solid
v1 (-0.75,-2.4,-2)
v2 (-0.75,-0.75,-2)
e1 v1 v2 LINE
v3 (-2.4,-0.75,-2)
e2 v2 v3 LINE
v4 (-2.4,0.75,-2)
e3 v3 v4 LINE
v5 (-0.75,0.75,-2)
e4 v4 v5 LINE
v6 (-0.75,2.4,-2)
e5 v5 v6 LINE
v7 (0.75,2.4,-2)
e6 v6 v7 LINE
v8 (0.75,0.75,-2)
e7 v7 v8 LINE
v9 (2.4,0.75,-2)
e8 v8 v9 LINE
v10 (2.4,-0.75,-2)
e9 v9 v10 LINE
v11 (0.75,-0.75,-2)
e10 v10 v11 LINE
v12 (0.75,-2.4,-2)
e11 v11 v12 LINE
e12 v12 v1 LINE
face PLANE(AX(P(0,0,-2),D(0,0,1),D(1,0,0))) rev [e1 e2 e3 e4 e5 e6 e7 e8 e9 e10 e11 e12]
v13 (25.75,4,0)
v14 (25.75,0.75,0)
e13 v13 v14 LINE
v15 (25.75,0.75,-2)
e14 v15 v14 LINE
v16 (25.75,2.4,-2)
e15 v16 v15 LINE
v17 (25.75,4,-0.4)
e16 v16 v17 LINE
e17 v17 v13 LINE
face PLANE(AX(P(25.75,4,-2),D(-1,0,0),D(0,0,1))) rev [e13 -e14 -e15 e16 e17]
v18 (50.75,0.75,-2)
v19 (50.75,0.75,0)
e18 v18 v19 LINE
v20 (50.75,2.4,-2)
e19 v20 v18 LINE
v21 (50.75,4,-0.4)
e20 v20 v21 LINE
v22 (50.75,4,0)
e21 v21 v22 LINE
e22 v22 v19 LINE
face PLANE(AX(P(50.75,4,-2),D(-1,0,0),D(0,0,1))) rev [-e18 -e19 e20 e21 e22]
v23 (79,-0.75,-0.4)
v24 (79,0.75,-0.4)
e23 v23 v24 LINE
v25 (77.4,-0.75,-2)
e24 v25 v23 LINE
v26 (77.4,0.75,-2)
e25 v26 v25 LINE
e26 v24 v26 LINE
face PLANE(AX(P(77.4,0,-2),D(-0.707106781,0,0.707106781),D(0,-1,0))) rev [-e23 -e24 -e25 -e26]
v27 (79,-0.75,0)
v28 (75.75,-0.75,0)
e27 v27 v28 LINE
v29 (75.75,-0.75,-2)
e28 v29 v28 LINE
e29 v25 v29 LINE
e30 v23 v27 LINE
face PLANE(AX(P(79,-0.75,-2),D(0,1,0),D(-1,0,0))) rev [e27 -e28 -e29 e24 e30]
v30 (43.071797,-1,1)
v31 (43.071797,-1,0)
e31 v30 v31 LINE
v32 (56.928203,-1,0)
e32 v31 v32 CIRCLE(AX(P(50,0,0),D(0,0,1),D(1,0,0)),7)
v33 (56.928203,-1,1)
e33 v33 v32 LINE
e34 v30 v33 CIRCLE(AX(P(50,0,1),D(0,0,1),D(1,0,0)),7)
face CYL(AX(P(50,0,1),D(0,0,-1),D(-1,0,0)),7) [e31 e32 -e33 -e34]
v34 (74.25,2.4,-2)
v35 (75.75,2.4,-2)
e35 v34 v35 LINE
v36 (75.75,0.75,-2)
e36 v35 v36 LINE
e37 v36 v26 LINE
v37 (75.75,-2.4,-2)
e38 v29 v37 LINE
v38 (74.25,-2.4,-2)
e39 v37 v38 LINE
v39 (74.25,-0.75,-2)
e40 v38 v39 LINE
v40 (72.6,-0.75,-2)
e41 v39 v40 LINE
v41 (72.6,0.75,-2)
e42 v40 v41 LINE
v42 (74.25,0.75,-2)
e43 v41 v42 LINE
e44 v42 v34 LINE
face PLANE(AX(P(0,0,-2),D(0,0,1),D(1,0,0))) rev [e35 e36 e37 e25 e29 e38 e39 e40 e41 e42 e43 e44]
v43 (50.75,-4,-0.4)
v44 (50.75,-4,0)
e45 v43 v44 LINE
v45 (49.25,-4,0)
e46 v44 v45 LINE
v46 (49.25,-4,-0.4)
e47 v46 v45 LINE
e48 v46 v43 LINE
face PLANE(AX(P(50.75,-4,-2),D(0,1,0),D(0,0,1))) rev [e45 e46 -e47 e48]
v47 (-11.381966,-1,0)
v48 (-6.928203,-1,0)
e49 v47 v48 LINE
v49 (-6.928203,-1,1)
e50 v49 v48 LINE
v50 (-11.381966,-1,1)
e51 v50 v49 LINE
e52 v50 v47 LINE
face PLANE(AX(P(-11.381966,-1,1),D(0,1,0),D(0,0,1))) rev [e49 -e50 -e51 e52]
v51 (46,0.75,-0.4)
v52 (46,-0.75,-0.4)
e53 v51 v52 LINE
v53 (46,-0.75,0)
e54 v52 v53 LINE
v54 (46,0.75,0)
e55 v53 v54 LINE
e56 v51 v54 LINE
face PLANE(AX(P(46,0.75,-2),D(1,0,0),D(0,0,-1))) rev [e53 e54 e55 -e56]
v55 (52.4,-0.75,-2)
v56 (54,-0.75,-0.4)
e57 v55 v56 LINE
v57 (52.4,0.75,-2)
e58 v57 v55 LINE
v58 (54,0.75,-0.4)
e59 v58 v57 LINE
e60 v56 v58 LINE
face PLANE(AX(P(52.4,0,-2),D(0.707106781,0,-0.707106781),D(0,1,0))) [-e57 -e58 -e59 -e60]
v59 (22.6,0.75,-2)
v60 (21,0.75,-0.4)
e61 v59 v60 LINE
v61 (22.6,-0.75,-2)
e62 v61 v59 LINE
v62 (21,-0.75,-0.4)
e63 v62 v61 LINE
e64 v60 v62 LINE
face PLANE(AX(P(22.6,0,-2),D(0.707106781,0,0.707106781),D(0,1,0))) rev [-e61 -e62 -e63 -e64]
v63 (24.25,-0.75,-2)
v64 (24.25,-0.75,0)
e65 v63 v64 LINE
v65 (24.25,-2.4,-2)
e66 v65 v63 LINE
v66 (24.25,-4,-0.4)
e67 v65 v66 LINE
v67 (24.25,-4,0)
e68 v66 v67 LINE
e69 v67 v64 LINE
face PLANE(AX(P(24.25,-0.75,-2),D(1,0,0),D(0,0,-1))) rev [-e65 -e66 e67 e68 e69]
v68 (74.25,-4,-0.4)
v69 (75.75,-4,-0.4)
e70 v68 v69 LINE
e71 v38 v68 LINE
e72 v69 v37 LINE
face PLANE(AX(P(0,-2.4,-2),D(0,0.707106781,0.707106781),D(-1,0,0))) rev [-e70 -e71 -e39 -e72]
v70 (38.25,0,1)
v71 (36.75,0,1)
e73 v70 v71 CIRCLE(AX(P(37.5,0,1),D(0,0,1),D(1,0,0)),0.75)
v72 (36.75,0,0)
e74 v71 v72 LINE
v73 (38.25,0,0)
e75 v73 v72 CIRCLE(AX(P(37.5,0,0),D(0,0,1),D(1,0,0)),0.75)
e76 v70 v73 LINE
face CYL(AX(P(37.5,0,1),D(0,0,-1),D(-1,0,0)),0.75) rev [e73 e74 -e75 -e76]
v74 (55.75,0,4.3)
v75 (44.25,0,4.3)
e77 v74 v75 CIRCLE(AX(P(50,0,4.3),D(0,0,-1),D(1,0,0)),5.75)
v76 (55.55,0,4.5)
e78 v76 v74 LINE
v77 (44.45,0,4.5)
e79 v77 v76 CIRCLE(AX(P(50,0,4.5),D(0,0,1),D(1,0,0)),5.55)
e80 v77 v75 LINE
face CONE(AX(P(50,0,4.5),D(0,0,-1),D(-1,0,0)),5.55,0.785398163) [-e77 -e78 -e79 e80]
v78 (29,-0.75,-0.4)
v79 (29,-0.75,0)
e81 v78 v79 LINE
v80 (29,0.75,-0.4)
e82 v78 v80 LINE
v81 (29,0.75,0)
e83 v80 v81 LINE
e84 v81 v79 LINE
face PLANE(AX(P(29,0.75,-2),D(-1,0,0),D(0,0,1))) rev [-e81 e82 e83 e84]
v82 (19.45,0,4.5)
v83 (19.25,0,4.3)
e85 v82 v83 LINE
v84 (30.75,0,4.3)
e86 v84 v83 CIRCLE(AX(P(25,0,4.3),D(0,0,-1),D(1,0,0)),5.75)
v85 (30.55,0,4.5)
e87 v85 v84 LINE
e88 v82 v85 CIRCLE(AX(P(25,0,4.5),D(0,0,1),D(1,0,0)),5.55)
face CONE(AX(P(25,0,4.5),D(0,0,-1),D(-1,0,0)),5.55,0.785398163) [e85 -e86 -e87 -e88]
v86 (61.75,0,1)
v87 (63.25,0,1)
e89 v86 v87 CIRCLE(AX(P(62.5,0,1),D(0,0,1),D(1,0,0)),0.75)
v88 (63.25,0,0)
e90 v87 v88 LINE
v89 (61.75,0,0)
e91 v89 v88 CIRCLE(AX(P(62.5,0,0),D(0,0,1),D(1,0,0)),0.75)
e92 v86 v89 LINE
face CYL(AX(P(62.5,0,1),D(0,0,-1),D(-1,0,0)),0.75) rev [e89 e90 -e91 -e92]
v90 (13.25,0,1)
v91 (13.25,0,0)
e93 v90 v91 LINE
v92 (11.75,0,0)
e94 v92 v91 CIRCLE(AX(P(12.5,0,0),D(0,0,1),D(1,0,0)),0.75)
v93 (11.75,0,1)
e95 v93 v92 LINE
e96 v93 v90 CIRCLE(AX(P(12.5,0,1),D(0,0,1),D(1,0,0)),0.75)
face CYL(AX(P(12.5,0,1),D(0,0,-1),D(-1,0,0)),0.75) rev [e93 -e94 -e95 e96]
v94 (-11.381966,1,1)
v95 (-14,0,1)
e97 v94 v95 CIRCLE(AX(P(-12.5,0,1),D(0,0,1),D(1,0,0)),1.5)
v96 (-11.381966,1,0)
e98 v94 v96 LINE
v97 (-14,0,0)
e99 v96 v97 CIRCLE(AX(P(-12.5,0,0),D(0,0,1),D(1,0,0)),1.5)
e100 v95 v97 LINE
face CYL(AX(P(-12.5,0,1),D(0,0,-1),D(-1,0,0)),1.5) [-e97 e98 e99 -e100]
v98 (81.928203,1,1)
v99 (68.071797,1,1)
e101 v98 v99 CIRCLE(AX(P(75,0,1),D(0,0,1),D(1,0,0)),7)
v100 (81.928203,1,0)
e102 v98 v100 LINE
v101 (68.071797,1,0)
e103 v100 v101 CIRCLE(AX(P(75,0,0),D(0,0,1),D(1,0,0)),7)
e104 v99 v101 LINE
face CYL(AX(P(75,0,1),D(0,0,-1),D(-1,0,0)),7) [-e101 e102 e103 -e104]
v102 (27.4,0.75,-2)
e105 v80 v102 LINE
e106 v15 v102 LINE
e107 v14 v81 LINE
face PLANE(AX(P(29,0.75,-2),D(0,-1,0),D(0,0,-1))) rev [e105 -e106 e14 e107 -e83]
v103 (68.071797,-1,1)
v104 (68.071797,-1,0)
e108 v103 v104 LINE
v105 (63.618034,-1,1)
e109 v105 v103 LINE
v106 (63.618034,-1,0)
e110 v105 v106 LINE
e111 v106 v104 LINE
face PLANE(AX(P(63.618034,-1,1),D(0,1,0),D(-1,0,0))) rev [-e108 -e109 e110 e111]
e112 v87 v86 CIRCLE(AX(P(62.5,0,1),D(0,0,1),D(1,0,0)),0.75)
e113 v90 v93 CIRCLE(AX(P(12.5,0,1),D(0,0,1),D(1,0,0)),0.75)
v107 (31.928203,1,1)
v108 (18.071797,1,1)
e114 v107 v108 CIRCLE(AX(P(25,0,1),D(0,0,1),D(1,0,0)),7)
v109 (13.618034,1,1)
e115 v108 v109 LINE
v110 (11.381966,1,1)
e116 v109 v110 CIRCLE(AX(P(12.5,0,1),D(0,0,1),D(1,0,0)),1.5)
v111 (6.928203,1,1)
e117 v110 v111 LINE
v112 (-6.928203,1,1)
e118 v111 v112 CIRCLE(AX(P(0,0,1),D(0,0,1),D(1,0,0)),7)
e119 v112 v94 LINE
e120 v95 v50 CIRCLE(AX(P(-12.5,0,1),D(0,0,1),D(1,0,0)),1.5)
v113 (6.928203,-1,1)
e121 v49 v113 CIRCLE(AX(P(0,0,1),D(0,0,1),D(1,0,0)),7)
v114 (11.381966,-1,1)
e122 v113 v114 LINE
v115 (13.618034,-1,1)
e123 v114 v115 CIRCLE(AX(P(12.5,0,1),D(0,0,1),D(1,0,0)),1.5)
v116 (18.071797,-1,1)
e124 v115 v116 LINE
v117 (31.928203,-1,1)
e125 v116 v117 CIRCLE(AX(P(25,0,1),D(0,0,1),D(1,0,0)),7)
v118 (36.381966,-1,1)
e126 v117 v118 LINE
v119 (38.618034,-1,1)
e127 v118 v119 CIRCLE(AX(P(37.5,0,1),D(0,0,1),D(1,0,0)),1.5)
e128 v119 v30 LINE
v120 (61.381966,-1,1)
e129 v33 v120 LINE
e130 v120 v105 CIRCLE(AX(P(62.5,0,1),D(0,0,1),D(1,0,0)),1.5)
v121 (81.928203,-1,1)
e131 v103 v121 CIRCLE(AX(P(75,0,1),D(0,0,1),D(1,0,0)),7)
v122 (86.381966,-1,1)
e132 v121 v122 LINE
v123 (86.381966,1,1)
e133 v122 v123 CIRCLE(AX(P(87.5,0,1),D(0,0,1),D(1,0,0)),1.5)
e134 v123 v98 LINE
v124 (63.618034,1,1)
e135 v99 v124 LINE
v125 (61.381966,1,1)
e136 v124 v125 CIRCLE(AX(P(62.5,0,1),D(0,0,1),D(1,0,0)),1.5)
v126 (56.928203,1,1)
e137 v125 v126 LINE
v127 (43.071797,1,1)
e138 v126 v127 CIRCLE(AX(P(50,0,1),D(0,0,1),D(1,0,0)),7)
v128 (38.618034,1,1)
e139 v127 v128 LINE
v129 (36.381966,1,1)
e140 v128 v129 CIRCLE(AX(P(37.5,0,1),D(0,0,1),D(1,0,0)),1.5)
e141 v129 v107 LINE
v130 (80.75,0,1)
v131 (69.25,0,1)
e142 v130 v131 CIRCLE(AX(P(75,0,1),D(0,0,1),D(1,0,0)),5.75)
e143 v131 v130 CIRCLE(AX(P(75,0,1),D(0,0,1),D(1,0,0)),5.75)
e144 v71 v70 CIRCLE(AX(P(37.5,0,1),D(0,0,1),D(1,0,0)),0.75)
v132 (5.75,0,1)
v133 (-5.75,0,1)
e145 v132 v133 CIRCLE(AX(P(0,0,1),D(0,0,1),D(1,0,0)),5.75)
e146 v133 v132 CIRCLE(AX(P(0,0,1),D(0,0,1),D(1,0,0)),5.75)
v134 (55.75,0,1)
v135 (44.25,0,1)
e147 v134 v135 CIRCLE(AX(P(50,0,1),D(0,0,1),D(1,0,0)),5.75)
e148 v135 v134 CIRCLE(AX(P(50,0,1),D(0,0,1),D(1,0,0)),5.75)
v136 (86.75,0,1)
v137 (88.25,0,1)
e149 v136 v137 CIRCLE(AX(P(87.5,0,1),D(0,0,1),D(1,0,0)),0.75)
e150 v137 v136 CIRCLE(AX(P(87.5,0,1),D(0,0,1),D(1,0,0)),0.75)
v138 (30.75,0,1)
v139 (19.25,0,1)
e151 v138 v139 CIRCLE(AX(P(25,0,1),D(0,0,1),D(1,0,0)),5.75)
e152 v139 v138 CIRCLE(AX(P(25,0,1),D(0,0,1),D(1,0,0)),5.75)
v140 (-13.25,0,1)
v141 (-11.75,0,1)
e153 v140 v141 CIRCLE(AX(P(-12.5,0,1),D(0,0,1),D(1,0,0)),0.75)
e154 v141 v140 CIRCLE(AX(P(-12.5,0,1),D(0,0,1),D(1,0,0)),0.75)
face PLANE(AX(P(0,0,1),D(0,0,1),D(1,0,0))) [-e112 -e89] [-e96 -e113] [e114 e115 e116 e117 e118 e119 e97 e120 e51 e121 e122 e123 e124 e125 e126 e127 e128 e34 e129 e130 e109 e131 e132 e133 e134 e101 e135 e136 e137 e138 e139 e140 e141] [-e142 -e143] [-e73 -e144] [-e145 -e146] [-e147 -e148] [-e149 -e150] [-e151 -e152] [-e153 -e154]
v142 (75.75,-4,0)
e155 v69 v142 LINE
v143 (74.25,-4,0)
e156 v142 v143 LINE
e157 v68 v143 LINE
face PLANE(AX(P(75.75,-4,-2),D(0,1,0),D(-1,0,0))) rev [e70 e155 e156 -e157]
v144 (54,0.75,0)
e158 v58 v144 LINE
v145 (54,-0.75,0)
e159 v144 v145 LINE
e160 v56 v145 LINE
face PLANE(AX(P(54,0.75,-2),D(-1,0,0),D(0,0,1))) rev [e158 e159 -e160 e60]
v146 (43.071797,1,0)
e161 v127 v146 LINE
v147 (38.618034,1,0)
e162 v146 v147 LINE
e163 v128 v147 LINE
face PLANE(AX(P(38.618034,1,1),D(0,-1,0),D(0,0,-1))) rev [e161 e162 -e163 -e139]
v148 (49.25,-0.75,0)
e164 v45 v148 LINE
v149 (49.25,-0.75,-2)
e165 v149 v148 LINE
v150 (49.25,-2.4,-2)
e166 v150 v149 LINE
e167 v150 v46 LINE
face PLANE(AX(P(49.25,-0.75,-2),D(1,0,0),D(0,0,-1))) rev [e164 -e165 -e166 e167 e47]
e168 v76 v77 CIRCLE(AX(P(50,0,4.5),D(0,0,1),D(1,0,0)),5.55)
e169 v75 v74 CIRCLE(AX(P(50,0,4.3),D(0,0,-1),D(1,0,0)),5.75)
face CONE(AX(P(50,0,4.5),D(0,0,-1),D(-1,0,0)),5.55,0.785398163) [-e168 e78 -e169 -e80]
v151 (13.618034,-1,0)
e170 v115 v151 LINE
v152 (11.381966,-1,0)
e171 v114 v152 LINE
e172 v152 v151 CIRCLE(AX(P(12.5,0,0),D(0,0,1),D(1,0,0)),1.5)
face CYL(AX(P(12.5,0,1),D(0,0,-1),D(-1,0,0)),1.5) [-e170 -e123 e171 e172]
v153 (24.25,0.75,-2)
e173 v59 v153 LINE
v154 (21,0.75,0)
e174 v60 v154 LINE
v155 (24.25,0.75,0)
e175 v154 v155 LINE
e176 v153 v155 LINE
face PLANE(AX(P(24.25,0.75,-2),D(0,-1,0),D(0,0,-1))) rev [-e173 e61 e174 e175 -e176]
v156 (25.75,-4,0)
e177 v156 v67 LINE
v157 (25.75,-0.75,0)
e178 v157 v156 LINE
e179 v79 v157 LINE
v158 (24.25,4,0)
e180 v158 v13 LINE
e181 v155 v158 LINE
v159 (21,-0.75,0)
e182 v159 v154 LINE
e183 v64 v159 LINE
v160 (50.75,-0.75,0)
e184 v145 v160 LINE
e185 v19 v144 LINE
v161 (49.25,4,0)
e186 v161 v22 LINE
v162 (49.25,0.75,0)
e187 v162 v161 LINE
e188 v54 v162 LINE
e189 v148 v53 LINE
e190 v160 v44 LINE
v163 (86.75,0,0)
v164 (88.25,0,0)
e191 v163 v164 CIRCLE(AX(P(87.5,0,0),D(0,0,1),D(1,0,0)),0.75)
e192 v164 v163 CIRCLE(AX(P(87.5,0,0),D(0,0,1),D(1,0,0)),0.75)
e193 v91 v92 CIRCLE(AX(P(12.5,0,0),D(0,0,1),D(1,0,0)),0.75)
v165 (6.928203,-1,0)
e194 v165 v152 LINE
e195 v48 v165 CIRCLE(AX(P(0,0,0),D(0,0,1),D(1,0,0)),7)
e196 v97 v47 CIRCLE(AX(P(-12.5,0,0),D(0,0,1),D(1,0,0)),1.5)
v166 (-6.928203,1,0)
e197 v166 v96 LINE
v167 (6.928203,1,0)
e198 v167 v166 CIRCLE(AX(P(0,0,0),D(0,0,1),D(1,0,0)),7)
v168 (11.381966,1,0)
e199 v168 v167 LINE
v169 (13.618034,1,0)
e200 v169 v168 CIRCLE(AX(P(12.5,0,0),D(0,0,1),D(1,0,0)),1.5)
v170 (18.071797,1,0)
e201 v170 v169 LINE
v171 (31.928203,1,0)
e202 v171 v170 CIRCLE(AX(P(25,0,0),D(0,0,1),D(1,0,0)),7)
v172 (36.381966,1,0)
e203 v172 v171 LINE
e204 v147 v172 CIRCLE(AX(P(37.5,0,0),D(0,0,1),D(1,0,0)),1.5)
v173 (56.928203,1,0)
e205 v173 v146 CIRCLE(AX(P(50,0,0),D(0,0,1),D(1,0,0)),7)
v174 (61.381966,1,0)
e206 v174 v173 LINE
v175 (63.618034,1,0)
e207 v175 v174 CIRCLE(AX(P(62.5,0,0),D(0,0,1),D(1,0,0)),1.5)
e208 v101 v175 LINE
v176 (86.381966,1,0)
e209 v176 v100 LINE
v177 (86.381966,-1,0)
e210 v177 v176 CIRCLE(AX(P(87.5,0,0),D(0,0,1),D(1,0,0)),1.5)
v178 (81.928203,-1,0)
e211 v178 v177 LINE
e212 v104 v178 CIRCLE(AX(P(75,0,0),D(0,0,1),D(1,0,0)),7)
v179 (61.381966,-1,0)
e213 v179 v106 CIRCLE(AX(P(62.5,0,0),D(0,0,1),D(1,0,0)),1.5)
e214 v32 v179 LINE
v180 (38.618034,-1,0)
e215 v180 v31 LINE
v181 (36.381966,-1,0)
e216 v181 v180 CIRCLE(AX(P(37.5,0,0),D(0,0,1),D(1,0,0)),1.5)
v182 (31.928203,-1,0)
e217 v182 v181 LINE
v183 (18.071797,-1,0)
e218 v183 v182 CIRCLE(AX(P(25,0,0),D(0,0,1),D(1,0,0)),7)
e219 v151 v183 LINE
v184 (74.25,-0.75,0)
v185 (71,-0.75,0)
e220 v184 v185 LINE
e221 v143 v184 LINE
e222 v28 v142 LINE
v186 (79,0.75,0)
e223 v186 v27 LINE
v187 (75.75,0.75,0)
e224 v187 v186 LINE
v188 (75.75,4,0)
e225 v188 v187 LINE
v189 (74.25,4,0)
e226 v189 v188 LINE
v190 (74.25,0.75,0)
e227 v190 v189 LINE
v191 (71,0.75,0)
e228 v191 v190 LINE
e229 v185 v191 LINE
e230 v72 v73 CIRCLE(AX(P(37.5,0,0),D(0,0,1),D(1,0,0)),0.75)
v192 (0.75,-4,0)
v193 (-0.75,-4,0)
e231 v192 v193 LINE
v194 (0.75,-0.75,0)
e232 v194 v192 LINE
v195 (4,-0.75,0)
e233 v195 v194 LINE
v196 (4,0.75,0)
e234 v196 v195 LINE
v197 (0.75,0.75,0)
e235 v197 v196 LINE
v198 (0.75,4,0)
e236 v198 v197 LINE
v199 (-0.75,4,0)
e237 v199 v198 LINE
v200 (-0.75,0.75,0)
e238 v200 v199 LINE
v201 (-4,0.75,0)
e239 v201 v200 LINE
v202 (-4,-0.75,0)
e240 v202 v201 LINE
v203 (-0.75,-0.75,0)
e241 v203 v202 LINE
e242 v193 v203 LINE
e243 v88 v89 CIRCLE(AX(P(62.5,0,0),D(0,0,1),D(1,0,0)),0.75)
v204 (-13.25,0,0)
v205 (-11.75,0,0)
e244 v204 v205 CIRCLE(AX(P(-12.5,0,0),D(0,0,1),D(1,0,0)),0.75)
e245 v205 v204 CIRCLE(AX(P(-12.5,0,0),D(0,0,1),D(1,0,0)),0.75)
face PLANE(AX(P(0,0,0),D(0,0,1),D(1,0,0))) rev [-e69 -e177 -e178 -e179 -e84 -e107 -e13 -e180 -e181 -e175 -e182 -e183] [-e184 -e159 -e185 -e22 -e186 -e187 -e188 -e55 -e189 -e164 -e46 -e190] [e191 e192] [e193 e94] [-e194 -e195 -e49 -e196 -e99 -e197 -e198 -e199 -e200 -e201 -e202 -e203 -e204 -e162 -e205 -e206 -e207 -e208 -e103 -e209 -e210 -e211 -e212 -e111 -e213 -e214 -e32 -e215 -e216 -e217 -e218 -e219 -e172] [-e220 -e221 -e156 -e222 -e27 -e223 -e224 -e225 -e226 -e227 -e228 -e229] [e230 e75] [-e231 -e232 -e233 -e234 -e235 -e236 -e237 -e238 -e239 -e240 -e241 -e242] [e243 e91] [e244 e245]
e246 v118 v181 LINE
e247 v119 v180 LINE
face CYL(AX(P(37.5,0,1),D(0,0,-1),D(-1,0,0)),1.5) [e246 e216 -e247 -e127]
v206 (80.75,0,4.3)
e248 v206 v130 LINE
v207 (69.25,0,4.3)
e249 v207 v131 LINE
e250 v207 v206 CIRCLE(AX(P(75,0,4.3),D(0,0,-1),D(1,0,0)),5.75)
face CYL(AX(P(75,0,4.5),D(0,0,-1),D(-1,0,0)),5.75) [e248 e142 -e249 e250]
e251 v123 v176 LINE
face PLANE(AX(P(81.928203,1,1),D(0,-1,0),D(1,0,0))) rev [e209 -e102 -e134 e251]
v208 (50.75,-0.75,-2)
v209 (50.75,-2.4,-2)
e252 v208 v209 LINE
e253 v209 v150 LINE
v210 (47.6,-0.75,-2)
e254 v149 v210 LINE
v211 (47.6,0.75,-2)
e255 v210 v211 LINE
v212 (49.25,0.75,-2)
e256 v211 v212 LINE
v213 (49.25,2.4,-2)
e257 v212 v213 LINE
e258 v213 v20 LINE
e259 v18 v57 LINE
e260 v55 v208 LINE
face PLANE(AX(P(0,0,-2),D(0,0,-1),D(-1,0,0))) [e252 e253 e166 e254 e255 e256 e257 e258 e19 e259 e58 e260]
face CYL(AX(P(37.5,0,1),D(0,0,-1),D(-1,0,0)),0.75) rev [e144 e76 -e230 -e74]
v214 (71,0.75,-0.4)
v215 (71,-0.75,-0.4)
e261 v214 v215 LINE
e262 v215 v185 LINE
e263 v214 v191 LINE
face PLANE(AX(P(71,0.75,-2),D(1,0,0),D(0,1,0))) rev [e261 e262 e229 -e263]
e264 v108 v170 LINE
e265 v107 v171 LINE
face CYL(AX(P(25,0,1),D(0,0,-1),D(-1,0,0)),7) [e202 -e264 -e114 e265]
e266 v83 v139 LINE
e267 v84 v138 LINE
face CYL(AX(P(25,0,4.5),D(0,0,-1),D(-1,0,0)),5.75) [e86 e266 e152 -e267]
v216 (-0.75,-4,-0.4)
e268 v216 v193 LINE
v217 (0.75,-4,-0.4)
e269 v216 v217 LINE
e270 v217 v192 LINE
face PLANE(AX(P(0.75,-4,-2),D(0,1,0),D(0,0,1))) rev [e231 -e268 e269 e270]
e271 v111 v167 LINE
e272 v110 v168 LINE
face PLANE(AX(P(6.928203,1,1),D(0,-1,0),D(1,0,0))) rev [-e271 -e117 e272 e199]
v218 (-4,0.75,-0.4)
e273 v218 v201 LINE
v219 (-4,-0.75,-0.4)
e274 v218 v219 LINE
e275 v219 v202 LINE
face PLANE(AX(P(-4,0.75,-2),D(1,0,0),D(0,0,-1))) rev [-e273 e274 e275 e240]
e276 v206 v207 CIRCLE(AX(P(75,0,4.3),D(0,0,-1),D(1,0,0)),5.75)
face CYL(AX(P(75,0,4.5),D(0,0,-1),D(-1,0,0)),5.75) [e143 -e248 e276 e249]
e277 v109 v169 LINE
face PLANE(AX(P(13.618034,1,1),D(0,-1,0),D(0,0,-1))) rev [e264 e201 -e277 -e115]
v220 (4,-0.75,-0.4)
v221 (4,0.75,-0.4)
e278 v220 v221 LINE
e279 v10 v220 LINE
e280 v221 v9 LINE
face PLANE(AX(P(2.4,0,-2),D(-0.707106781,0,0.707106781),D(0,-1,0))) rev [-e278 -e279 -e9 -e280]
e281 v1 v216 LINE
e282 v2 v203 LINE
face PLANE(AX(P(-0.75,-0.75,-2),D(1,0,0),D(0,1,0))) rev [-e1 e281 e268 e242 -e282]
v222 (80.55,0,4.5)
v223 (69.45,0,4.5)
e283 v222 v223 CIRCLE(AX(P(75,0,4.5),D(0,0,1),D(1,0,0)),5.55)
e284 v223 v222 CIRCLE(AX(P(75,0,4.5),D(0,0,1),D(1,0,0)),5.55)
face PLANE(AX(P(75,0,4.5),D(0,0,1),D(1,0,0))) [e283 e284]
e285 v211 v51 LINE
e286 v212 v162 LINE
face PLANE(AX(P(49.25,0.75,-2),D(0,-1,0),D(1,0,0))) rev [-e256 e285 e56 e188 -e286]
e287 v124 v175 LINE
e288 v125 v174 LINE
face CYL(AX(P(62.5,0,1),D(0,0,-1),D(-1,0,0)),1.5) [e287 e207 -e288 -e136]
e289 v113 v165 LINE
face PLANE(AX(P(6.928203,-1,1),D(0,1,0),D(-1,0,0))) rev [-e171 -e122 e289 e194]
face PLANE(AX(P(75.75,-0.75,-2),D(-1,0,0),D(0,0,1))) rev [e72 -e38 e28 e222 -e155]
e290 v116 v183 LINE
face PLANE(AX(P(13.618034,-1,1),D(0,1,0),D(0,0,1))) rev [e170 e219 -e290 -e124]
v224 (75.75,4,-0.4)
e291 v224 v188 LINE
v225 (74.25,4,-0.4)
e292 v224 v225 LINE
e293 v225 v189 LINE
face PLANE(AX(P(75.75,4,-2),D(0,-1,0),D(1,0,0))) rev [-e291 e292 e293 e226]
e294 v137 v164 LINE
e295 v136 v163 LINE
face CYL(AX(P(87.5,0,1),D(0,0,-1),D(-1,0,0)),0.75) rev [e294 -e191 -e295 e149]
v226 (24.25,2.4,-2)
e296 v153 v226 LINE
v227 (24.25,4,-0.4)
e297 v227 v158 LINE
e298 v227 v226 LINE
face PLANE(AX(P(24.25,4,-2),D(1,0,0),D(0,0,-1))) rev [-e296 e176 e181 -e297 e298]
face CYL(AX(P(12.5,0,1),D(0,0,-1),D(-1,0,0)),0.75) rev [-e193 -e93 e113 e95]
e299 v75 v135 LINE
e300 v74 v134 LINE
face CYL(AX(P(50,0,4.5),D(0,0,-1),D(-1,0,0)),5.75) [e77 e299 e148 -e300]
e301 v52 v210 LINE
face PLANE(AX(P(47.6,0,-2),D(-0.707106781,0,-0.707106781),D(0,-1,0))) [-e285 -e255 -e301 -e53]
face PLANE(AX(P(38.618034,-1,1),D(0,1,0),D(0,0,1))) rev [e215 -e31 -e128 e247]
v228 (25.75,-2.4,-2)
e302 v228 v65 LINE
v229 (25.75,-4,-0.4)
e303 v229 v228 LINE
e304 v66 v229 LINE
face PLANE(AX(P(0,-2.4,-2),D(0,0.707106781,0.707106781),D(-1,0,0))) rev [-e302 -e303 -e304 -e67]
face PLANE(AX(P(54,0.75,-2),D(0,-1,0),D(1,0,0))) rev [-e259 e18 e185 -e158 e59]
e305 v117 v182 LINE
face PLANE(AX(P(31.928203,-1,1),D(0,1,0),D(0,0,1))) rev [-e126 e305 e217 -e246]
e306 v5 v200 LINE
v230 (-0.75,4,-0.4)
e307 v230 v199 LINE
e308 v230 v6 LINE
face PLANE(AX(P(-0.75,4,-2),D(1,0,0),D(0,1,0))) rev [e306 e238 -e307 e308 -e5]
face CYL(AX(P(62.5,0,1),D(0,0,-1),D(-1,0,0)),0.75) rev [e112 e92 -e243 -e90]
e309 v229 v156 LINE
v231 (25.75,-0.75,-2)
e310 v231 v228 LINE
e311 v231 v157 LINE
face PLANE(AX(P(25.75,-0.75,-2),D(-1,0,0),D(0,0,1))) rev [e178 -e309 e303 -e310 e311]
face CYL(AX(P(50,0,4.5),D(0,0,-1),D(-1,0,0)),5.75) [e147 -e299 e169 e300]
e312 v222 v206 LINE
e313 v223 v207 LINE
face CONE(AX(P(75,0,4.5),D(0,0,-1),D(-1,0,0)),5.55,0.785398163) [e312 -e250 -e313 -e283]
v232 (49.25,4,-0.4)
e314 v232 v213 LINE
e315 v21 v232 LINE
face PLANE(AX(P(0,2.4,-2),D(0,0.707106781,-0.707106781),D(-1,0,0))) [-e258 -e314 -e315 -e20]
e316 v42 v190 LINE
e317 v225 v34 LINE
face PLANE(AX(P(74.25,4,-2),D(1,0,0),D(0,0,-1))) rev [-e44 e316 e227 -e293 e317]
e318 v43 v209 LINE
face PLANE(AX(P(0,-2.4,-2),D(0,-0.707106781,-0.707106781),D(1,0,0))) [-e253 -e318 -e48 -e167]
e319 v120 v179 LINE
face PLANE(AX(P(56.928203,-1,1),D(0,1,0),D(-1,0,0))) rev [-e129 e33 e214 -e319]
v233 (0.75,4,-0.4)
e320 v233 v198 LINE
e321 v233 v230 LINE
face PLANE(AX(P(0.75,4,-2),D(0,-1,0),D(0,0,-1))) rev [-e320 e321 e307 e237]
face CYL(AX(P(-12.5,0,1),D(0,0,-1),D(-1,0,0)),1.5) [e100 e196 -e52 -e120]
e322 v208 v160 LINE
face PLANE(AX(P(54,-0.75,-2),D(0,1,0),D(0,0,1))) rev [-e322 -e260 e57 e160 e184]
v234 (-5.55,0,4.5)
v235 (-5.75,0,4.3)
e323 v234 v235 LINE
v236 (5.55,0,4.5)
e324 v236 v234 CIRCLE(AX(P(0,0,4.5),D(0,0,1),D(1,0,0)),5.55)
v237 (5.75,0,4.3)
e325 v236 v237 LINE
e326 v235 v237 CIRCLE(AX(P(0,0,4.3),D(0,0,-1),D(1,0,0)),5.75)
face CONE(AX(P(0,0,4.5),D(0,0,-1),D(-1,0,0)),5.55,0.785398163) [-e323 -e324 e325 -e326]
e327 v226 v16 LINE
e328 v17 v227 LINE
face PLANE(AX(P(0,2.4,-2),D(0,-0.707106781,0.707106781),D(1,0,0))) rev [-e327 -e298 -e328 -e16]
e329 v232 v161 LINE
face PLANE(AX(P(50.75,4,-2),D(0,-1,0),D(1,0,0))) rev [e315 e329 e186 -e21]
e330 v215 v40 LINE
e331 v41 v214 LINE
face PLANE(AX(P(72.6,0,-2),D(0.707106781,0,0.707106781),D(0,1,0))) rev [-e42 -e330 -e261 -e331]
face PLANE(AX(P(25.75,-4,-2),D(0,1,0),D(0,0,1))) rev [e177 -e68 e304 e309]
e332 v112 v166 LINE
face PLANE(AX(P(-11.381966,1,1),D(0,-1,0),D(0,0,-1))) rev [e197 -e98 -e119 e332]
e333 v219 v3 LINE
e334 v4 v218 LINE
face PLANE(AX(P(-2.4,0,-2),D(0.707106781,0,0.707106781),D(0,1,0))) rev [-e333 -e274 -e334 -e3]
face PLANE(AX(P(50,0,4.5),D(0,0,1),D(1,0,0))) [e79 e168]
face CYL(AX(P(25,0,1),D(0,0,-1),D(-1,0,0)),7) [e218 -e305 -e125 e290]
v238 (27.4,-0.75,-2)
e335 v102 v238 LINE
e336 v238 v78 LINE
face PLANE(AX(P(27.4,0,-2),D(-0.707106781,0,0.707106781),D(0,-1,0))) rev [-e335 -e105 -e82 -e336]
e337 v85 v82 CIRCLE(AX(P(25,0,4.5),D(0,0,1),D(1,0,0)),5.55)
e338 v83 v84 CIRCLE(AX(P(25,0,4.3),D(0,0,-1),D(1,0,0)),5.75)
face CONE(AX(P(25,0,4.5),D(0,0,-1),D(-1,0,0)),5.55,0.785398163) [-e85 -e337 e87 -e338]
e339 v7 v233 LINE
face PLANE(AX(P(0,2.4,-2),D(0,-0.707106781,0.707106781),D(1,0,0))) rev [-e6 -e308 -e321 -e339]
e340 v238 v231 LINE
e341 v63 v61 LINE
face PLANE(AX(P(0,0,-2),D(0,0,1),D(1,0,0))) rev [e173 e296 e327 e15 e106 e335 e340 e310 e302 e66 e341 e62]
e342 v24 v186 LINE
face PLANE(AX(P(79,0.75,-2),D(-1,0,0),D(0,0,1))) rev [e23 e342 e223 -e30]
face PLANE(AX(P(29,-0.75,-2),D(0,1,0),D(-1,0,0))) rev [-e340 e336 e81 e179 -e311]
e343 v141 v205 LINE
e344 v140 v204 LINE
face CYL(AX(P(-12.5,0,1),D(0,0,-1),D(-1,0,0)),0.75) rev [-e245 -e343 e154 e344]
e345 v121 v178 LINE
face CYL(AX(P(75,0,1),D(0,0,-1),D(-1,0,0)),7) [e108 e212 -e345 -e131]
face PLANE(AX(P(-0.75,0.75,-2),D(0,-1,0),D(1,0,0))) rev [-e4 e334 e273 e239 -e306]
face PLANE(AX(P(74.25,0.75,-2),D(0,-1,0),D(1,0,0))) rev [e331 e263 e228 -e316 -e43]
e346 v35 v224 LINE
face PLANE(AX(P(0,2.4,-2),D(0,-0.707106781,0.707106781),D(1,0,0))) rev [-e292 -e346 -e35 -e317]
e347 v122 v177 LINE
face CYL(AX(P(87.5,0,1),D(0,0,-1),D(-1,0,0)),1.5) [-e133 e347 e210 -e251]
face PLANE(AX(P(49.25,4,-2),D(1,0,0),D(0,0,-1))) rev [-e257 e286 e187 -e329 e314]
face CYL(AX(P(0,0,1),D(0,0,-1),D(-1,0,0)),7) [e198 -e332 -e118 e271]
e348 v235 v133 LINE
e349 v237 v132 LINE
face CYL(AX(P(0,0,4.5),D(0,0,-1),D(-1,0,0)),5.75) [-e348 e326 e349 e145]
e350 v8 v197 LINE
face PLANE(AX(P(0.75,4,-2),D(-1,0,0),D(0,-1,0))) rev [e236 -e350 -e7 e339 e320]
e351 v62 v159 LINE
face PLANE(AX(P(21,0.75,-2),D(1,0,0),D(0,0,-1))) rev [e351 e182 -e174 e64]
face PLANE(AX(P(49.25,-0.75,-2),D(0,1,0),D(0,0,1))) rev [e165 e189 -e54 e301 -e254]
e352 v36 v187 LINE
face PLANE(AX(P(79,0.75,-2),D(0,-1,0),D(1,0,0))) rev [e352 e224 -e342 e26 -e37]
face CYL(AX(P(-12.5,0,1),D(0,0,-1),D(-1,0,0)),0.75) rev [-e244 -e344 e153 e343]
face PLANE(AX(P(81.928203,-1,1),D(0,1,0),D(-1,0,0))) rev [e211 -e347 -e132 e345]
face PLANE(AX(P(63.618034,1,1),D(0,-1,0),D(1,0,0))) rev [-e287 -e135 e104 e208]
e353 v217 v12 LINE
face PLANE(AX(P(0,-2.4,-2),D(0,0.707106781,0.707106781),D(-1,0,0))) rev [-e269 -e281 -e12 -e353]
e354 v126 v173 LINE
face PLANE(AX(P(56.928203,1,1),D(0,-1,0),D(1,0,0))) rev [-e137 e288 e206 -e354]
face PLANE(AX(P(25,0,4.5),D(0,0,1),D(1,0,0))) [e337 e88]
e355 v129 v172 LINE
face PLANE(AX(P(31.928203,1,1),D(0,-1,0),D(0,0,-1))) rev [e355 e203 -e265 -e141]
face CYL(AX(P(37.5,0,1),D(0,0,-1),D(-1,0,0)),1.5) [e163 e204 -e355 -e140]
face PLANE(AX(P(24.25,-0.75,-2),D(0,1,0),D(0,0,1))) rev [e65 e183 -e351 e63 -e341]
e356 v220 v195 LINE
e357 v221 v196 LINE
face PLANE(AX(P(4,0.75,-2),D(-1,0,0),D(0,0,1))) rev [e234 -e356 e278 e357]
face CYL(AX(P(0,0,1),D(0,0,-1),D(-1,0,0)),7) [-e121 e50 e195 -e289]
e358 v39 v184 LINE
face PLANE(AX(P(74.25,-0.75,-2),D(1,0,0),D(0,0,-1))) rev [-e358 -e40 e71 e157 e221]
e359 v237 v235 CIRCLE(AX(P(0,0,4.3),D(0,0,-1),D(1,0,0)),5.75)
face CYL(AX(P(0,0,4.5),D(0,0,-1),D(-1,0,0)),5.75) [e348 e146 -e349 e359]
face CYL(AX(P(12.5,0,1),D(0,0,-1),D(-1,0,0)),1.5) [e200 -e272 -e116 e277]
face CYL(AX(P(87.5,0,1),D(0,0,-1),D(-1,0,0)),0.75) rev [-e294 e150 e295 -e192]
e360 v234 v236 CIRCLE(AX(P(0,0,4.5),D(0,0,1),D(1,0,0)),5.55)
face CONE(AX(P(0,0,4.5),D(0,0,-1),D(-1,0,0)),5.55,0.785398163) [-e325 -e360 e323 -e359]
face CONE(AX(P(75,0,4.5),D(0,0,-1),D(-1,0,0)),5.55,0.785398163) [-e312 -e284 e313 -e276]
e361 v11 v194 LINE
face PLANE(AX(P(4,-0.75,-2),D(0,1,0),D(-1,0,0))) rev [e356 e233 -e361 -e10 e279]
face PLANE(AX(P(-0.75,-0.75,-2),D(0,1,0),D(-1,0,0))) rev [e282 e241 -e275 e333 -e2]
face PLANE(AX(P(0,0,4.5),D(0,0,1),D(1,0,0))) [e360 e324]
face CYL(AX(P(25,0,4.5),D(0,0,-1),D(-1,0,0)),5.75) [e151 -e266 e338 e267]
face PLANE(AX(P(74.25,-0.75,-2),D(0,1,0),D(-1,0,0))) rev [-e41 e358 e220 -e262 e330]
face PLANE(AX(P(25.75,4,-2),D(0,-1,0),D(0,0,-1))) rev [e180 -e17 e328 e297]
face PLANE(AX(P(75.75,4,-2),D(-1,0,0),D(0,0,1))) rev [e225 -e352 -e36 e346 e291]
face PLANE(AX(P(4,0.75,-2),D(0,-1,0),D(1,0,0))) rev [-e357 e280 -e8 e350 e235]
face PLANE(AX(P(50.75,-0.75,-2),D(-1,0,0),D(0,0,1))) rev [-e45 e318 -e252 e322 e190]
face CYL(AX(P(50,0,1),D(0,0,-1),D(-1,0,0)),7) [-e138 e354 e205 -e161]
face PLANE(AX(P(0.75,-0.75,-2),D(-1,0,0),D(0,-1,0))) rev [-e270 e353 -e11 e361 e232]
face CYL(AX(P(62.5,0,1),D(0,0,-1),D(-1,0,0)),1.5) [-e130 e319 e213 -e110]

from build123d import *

# Parameters (mm, degrees)
SKETCH1_R           = 0.75
BOSS_EXTRUDE1_DEPTH = 1
SKETCH2_R           = 5.75
BOSS_EXTRUDE2_DEPTH = 3.5
CHAMFER1_SIZE       = 0.2
BOSS_EXTRUDE3_DEPTH = 2
CHAMFER2_SIZE       = 1.6


with BuildPart() as part:
    # Sketch1 → Boss-Extrude1 (new body)
    with BuildSketch(Plane.XY):
        with BuildLine():
            Line((-11.381966011, 1), (-6.92820323, 1))
            ThreePointArc((-6.92820323, 1), (0, 7), (6.92820323, 1))
            Line((6.92820323, 1), (11.381966011, 1))
            ThreePointArc((11.381966011, 1), (12.5, 1.5), (13.618033989, 1))
            Line((13.618033989, 1), (18.07179677, 1))
            ThreePointArc((18.07179677, 1), (25, 7), (31.92820323, 1))
            Line((31.92820323, 1), (36.381966011, 1))
            ThreePointArc((36.381966011, 1), (37.5, 1.5), (38.618033989, 1))
            Line((38.618033989, 1), (43.07179677, 1))
            ThreePointArc((43.07179677, 1), (50, 7), (56.92820323, 1))
            Line((56.92820323, 1), (61.381966011, 1))
            ThreePointArc((61.381966011, 1), (62.5, 1.5), (63.618033989, 1))
            Line((63.618033989, 1), (68.07179677, 1))
            ThreePointArc((68.07179677, 1), (75, 7), (81.92820323, 1))
            Line((81.92820323, 1), (86.381966011, 1))
            ThreePointArc((86.381966011, 1), (89, 0), (86.381966011, -1))
            Line((86.381966011, -1), (81.92820323, -1))
            ThreePointArc((81.92820323, -1), (75, -7), (68.07179677, -1))
            Line((68.07179677, -1), (63.618033989, -1))
            ThreePointArc((63.618033989, -1), (62.5, -1.5), (61.381966011, -1))
            Line((61.381966011, -1), (56.92820323, -1))
            ThreePointArc((56.92820323, -1), (50, -7), (43.07179677, -1))
            Line((43.07179677, -1), (38.618033989, -1))
            ThreePointArc((38.618033989, -1), (37.5, -1.5), (36.381966011, -1))
            Line((36.381966011, -1), (31.92820323, -1))
            ThreePointArc((31.92820323, -1), (25, -7), (18.07179677, -1))
            Line((18.07179677, -1), (13.618033989, -1))
            ThreePointArc((13.618033989, -1), (12.5, -1.5), (11.381966011, -1))
            Line((11.381966011, -1), (6.92820323, -1))
            ThreePointArc((6.92820323, -1), (0, -7), (-6.92820323, -1))
            Line((-6.92820323, -1), (-11.381966011, -1))
            ThreePointArc((-11.381966011, -1), (-14, 0), (-11.381966011, 1))
        make_face()
        with Locations((12.5, 0)):
            Circle(SKETCH1_R, mode=Mode.SUBTRACT)
        with Locations((37.5, 0)):
            Circle(SKETCH1_R, mode=Mode.SUBTRACT)
        with Locations((62.5, 0)):
            Circle(SKETCH1_R, mode=Mode.SUBTRACT)
        with Locations((-12.5, 0)):
            Circle(SKETCH1_R, mode=Mode.SUBTRACT)
        with Locations((87.5, 0)):
            Circle(SKETCH1_R, mode=Mode.SUBTRACT)
    extrude(amount=BOSS_EXTRUDE1_DEPTH)

    # Sketch2 → Boss-Extrude2 (add)
    with BuildSketch(Plane.XY.offset(1)):
        Circle(SKETCH2_R)
        with Locations((25, 0)):
            Circle(SKETCH2_R)
        with Locations((50, 0)):
            Circle(SKETCH2_R)
        with Locations((75, 0)):
            Circle(SKETCH2_R)
    extrude(amount=BOSS_EXTRUDE2_DEPTH)

    # Chamfer1
    chamfer1_edges = [part.edges().sort_by_distance(p)[0] for p in [
        (-5.75, 0, 4.5),
        (19.25, 0, 4.5),
        (44.25, 0, 4.5),
        (69.25, 0, 4.5),
    ]]
    chamfer(chamfer1_edges, length=CHAMFER1_SIZE)

    # Sketch3 → Boss-Extrude3 (add)
    with BuildSketch(Plane(origin=(0, 0, 0), x_dir=(-1, 0, 0), z_dir=(0, 0, -1))):
        Polygon((-74.25, -0.75), (-74.25, -4), (-75.75, -4), (-75.75, -0.75), (-79, -0.75), (-79, 0.75), (-75.75, 0.75), (-75.75, 4), (-74.25, 4), (-74.25, 0.75), (-71, 0.75), (-71, -0.75), align=None)
        Polygon((-50.75, 4), (-49.25, 4), (-49.25, 0.75), (-46, 0.75), (-46, -0.75), (-49.25, -0.75), (-49.25, -4), (-50.75, -4), (-50.75, -0.75), (-54, -0.75), (-54, 0.75), (-50.75, 0.75), align=None)
        Polygon((-29, 0.75), (-25.75, 0.75), (-25.75, 4), (-24.25, 4), (-24.25, 0.75), (-21, 0.75), (-21, -0.75), (-24.25, -0.75), (-24.25, -4), (-25.75, -4), (-25.75, -0.75), (-29, -0.75), align=None)
        Polygon((-4, 0.75), (-0.75, 0.75), (-0.75, 4), (0.75, 4), (0.75, 0.75), (4, 0.75), (4, -0.75), (0.75, -0.75), (0.75, -4), (-0.75, -4), (-0.75, -0.75), (-4, -0.75), align=None)
    extrude(amount=BOSS_EXTRUDE3_DEPTH)

    # Chamfer2
    chamfer2_edges = [part.edges().sort_by_distance(p)[0] for p in [
        (75, -4, -2),
        (71, 0, -2),
        (75, 4, -2),
        (79, 0, -2),
        (46, 0, -2),
        (50, 4, -2),
        (54, 0, -2),
        (50, -4, -2),
        (21, 0, -2),
        (25, 4, -2),
        (29, 0, -2),
        (25, -4, -2),
        (-4, 0, -2),
        (0, 4, -2),
        (4, 0, -2),
        (0, -4, -2),
    ]]
    chamfer(chamfer2_edges, length=CHAMFER2_SIZE)


solid = part.part
